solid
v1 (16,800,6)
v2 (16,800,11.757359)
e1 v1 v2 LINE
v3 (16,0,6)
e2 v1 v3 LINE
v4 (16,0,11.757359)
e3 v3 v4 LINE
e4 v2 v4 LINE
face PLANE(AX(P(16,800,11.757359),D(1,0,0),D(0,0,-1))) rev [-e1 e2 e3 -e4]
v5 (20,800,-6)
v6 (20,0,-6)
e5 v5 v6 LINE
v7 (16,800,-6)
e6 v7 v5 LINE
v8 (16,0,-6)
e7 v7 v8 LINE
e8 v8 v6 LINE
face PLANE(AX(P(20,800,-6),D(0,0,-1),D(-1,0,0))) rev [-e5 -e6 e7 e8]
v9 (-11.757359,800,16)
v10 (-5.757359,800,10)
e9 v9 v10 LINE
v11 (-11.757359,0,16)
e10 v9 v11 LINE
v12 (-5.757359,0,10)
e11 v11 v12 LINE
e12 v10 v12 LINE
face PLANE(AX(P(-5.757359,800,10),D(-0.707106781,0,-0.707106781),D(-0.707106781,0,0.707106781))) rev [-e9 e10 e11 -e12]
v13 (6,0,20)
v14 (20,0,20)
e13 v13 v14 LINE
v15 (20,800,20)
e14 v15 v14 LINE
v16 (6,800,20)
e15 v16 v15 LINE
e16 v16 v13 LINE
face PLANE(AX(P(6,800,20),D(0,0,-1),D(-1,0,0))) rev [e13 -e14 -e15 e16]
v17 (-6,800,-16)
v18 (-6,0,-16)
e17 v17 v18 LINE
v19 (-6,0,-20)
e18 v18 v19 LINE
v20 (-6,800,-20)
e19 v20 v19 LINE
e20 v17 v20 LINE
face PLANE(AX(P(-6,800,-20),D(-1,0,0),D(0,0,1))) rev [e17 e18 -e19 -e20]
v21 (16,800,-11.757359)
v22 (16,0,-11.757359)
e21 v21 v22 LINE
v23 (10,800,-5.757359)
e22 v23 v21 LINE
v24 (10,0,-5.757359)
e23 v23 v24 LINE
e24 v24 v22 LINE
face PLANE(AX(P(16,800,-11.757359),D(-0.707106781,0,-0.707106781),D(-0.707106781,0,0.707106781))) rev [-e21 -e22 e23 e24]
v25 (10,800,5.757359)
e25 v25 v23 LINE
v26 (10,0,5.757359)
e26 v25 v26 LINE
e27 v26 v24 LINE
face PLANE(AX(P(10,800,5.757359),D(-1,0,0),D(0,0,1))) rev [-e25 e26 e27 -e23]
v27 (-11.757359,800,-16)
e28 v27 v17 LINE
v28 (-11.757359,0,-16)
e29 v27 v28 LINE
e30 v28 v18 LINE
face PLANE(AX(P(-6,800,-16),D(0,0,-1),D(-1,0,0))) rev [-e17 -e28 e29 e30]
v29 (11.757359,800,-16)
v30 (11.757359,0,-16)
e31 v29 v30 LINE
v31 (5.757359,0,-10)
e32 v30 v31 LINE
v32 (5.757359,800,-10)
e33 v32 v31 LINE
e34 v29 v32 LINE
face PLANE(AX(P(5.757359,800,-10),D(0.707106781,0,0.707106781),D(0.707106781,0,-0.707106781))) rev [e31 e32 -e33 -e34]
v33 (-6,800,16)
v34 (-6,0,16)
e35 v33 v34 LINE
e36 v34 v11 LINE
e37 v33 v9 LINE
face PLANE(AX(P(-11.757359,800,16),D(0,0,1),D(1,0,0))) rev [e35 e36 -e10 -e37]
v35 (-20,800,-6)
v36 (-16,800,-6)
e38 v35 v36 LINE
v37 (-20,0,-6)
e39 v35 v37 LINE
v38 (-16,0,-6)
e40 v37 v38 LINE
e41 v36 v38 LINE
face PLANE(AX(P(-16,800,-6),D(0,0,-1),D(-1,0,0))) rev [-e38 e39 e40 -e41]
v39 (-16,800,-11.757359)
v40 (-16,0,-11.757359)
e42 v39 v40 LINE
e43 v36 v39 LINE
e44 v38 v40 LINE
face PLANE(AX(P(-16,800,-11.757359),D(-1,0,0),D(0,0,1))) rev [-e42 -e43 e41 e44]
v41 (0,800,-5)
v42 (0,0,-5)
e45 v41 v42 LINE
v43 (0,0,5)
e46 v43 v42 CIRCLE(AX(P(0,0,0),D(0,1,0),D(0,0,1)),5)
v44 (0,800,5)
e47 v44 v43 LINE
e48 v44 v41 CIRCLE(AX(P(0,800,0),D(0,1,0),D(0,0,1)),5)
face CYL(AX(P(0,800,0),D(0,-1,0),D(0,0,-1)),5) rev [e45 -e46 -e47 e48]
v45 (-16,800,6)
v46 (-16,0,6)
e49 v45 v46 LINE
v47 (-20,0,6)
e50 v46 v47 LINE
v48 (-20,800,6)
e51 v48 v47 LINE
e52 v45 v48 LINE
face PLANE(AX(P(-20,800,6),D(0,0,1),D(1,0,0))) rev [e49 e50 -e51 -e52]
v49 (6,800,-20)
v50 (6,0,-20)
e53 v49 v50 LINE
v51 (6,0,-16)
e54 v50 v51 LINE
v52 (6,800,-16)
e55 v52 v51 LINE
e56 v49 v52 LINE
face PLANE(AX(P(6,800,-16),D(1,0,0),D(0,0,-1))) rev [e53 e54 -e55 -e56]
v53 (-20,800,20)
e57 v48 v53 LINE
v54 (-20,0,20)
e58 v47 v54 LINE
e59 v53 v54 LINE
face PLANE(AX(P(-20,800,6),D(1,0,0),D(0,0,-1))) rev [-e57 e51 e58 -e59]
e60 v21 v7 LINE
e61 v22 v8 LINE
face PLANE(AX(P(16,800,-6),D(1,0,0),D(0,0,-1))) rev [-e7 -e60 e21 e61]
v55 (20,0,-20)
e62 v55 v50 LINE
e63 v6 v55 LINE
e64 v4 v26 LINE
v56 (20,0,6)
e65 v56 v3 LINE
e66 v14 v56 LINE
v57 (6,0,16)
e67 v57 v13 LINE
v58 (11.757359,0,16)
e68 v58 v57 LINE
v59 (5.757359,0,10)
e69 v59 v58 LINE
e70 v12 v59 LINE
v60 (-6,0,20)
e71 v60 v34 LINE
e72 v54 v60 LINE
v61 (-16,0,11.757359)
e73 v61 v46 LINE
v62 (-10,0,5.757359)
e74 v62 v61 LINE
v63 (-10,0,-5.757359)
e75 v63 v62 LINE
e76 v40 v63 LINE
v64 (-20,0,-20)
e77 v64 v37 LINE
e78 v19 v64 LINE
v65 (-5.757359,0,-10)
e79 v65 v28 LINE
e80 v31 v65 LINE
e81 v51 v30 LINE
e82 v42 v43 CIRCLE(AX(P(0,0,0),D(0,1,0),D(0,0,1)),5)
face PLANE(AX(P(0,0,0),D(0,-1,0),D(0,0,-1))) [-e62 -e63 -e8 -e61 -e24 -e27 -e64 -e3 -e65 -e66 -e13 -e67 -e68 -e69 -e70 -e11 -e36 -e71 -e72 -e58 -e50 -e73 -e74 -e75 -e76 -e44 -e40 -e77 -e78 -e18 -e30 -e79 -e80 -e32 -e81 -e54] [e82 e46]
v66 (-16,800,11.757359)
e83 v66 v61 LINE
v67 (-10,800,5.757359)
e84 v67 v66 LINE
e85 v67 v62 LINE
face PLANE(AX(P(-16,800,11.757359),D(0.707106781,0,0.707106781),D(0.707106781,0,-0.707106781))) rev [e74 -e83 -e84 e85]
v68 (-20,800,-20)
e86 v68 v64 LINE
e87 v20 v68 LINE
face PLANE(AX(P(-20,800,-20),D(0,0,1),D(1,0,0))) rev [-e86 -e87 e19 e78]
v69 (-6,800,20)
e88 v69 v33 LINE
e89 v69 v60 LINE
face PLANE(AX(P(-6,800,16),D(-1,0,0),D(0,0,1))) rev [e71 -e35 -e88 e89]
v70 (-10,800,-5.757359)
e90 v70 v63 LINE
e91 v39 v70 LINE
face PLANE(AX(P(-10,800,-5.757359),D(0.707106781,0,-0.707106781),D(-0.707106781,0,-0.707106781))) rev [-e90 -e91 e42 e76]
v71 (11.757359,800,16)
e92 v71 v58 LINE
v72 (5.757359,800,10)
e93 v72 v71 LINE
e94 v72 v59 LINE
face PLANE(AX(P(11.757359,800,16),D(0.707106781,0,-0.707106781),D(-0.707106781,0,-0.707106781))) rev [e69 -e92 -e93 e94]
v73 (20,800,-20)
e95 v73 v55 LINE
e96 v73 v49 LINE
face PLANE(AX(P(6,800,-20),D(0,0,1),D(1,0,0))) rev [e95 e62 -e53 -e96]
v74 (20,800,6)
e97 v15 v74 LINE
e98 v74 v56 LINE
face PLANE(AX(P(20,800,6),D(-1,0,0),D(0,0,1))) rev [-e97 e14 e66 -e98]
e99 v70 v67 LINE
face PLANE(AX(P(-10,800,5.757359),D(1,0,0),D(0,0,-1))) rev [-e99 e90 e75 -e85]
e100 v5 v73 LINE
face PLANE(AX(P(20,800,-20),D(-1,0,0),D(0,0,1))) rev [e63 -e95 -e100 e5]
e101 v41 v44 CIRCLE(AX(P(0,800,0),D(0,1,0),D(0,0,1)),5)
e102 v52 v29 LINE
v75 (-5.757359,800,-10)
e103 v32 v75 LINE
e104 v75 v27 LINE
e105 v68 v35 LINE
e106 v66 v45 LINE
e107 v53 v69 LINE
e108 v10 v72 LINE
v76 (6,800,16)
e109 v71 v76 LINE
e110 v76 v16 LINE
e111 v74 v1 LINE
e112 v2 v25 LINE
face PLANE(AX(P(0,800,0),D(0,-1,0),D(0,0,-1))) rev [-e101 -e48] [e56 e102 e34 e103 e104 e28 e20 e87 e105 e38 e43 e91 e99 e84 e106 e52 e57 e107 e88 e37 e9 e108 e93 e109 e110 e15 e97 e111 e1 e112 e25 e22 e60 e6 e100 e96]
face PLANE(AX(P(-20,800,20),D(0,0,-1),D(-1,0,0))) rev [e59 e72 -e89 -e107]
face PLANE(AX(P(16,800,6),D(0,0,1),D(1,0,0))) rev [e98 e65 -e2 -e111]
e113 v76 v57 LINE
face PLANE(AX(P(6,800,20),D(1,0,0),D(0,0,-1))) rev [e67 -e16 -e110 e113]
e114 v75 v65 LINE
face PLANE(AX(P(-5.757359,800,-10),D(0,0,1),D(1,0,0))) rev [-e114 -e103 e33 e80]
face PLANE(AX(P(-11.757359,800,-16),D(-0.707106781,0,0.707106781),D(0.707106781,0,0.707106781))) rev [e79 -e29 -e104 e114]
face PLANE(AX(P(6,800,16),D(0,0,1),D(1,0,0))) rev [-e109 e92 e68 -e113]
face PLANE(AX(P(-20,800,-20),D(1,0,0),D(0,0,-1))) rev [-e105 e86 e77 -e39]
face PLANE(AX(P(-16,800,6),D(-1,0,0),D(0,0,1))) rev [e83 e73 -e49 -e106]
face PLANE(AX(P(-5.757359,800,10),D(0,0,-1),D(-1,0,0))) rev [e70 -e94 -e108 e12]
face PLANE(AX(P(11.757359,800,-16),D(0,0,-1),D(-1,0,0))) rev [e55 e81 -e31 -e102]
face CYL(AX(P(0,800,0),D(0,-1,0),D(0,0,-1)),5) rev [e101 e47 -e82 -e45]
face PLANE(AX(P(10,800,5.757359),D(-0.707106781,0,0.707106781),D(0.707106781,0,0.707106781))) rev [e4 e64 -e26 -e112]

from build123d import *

# Parameters (mm, degrees)
SKETCH1_R           = 5
BOSS_EXTRUDE1_DEPTH = 800


with BuildPart() as part:
    # Sketch1 → Boss-Extrude1 (new body)
    with BuildSketch(Plane(origin=(0, 0, 0), x_dir=(1, 0, 0), z_dir=(0, 1, 0))):
        Polygon((-6, 20), (-6, 16), (-11.757359313, 16), (-5.757359313, 10), (5.757359313, 10), (11.757359313, 16), (6, 16), (6, 20), (20, 20), (20, 6), (16, 6), (16, 11.757359313), (10, 5.757359313), (10, -5.757359313), (16, -11.757359313), (16, -6), (20, -6), (20, -20), (6, -20), (6, -16), (11.757359313, -16), (5.757359313, -10), (-5.757359313, -10), (-11.757359313, -16), (-6, -16), (-6, -20), (-20, -20), (-20, -6), (-16, -6), (-16, -11.757359313), (-10, -5.757359313), (-10, 5.757359313), (-16, 11.757359313), (-16, 6), (-20, 6), (-20, 20), align=None)
        with Locations(Location((0, 0, 0), (0, 0, 270))):
            Circle(SKETCH1_R, mode=Mode.SUBTRACT)
    extrude(amount=BOSS_EXTRUDE1_DEPTH)


solid = part.part
